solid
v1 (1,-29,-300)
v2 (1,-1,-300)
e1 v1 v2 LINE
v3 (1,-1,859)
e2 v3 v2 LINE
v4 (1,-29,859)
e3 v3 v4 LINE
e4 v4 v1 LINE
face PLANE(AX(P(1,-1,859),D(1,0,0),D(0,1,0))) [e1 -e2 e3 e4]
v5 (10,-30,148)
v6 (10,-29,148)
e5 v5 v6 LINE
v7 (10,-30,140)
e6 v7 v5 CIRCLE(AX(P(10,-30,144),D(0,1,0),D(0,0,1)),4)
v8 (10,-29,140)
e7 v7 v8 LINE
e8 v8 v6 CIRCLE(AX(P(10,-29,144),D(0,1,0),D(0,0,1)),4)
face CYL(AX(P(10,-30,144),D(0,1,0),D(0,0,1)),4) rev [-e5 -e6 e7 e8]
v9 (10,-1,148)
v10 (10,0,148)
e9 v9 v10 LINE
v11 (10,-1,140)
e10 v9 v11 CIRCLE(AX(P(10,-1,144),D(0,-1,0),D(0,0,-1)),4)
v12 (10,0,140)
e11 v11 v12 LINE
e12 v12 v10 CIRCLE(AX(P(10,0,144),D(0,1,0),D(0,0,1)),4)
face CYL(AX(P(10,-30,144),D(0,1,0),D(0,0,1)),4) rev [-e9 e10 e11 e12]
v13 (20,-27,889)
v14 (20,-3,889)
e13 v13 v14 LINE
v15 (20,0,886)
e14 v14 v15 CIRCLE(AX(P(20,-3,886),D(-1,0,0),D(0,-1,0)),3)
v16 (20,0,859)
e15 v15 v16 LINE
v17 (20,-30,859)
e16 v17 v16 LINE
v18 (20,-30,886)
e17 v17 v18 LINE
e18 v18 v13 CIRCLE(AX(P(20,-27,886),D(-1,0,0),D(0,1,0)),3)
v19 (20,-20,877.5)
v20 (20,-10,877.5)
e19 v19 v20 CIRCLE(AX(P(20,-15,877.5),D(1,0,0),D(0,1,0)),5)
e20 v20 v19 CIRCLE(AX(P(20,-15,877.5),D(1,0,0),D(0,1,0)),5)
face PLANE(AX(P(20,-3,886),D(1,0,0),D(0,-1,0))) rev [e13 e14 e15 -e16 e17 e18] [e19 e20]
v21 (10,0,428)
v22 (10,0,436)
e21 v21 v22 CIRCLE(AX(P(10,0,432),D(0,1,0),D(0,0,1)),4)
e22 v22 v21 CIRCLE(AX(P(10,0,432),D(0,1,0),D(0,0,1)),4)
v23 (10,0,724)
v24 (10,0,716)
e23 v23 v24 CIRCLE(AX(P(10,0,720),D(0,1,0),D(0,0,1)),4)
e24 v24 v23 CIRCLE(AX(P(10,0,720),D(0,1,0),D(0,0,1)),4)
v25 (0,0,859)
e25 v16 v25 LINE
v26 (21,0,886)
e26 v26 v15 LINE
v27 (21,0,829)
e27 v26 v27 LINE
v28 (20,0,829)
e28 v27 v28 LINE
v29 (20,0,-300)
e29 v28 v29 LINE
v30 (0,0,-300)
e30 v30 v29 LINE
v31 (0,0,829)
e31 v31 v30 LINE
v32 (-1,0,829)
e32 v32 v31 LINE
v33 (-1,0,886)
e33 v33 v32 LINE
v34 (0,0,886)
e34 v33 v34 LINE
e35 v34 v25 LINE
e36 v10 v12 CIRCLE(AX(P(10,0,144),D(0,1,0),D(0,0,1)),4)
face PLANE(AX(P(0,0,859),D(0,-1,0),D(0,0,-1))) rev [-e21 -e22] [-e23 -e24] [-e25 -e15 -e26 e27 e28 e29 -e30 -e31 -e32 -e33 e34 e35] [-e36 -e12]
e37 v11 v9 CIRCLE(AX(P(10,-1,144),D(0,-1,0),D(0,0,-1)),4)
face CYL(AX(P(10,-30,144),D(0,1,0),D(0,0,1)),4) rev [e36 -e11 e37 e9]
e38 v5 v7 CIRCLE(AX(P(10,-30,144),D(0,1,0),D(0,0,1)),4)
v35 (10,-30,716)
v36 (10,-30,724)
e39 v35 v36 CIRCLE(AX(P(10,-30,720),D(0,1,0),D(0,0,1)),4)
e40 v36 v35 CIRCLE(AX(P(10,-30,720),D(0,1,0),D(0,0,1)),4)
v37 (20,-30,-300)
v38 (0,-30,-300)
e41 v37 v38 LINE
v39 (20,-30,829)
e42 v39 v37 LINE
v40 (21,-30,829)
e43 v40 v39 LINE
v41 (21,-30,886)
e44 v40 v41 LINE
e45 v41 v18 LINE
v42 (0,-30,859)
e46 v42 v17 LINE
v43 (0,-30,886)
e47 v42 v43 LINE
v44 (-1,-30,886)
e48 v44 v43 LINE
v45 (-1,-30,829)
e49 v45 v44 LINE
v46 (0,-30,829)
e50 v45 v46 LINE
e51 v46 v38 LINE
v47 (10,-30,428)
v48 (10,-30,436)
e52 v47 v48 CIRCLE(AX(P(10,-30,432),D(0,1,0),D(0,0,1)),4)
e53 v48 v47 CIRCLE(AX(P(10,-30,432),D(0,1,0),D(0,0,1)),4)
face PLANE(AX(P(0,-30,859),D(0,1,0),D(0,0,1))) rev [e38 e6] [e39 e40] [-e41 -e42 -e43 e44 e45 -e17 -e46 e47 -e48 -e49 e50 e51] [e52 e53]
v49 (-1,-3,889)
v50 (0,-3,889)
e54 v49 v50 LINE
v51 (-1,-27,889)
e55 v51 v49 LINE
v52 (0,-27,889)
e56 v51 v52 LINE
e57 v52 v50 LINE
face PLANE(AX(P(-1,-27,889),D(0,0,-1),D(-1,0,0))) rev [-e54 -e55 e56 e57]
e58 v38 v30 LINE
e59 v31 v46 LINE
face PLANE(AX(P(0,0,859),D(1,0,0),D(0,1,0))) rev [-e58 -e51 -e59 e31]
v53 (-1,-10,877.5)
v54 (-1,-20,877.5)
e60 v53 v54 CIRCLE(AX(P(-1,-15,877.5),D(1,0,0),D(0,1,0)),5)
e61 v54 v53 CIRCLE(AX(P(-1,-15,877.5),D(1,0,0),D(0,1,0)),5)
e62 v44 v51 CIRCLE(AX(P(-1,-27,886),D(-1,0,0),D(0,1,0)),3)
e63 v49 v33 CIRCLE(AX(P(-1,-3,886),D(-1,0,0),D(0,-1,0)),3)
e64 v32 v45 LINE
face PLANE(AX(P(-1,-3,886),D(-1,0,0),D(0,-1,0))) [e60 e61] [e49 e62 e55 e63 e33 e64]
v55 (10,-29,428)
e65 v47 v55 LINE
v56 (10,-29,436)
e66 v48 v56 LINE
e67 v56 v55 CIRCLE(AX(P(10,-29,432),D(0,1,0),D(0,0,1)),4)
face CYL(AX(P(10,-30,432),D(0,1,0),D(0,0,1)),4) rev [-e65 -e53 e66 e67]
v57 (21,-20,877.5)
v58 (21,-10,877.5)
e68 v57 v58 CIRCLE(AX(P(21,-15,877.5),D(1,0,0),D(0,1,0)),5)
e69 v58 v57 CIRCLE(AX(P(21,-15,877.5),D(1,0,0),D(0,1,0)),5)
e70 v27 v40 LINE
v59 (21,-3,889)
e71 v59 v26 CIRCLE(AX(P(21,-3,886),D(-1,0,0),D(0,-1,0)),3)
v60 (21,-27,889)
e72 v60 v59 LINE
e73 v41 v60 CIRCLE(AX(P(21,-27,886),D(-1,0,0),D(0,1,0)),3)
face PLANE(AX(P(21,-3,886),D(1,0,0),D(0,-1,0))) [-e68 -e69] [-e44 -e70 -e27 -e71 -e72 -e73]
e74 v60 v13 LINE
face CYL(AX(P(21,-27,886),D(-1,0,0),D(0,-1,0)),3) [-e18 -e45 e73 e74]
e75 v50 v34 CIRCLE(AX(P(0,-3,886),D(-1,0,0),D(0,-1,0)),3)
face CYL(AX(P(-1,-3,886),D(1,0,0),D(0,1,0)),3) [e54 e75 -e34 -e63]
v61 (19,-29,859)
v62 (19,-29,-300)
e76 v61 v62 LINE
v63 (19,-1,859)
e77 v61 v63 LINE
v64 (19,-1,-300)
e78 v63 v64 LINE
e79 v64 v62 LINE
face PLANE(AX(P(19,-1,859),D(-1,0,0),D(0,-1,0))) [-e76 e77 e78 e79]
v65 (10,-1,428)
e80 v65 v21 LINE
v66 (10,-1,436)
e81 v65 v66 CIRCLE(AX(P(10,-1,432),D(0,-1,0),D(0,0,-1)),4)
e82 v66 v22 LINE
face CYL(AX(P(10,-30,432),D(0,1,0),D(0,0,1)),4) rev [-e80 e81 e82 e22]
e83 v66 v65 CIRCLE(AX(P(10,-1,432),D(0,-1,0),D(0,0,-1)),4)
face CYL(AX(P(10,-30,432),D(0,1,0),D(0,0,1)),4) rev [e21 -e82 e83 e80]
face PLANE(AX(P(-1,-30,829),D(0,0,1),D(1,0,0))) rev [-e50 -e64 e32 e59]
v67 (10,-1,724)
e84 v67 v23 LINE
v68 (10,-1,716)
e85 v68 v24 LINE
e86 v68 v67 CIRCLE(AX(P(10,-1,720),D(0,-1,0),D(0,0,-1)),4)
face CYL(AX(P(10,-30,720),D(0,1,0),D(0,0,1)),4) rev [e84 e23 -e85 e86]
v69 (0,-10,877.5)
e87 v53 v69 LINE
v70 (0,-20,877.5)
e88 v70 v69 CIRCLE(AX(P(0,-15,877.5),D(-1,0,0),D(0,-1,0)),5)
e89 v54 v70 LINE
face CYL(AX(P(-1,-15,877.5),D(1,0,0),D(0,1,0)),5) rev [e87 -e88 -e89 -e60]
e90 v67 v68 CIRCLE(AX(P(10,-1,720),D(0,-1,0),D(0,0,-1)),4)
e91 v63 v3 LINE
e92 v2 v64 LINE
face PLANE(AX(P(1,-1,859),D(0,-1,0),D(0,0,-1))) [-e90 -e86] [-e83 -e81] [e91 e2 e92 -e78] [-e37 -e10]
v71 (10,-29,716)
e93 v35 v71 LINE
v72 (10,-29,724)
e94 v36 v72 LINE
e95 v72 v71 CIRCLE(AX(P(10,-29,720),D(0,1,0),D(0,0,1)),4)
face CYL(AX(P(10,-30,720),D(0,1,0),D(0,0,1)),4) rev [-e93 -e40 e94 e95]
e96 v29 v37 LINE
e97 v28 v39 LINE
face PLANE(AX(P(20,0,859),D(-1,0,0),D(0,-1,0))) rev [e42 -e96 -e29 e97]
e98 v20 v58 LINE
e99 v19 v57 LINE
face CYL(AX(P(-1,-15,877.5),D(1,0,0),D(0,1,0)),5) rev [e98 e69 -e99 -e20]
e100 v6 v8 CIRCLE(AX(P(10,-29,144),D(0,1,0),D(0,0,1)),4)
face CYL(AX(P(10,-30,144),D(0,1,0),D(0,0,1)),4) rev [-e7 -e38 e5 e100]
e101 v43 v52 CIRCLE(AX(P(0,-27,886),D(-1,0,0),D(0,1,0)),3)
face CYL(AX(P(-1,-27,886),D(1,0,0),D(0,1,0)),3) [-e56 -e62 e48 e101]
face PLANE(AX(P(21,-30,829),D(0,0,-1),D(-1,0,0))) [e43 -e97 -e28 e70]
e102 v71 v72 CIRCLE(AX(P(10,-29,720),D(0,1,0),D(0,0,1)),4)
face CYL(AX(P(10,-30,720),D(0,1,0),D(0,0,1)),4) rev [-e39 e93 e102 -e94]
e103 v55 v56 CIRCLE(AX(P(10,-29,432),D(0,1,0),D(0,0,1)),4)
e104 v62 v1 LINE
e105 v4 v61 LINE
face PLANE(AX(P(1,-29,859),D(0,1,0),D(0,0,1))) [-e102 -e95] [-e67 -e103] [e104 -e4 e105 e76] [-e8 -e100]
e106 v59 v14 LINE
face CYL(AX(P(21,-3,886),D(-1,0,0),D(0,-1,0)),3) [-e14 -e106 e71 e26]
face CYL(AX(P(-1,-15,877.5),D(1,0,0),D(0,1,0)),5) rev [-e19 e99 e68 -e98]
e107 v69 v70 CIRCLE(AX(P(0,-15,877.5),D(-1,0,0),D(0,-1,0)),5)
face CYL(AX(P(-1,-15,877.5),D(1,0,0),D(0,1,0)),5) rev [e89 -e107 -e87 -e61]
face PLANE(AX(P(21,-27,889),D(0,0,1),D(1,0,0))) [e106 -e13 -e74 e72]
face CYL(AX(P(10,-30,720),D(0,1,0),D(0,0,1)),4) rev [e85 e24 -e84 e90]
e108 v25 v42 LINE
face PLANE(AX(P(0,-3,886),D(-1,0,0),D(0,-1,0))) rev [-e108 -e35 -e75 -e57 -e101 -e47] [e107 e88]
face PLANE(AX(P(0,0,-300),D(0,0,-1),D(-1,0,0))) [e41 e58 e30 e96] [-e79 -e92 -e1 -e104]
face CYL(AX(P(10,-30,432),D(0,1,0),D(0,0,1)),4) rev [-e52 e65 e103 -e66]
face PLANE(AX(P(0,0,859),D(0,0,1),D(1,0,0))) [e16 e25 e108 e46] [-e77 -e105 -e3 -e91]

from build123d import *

# Parameters (mm, degrees)
SKETCH1_W           = 20
SKETCH1_H           = 30
SKETCH1_W_2         = 18
SKETCH1_H_2         = 28
BOSS_EXTRUDE1_DEPTH = 859
BOSS_EXTRUDE2_DEPTH = 1
SKETCH4_R           = 5
CUT_EXTRUDE1_DEPTH  = 890.778062216
SKETCH5_R           = 4
CUT_EXTRUDE2_DEPTH  = 890.753898558
SKETCH6_W           = 20
SKETCH6_H           = 30
SKETCH6_W_2         = 18
SKETCH6_H_2         = 28
BOSS_EXTRUDE3_DEPTH = 300


with BuildPart() as part:
    # Sketch1 → Boss-Extrude1 (new body)
    with BuildSketch(Plane.XY):
        with Locations((10, -15)):
            Rectangle(SKETCH1_W, SKETCH1_H)
        with Locations((10, -15)):
            Rectangle(SKETCH1_W_2, SKETCH1_H_2, mode=Mode.SUBTRACT)
    extrude(amount=BOSS_EXTRUDE1_DEPTH)

    # Sketch3 → Boss-Extrude2 (add)
    with BuildSketch(Plane.ZY):
        with BuildLine():
            Line((829, -30), (859, -30))
            Line((859, -30), (886, -30))
            ThreePointArc((886, -30), (888.121320344, -29.121320344), (889, -27))
            Line((889, -27), (889, -3))
            ThreePointArc((889, -3), (888.121320344, -0.878679656), (886, 0))
            Line((886, 0), (859, 0))
            Line((859, 0), (829, 0))
            Line((829, 0), (829, -30))
        make_face()
    boss_extrude2 = extrude(amount=BOSS_EXTRUDE2_DEPTH)

    # Mirror2: Boss-Extrude2 across plane
    add(boss_extrude2.mirror(Plane(origin=(10, 0, 0), x_dir=(0, 0, 1), z_dir=(1, 0, 0))))

    # Sketch4 → Cut-Extrude1 (cut, through all)
    with BuildSketch(Plane(origin=(21, 0, 0), x_dir=(0, 0, -1), z_dir=(1, 0, 0))):
        with Locations(Location((-877.5, -15, 0), (0, 0, 90))):
            Circle(SKETCH4_R)
    extrude(amount=-CUT_EXTRUDE1_DEPTH, mode=Mode.SUBTRACT)

    # Sketch5 → Cut-Extrude2 (cut, through all)
    with BuildSketch(Plane(origin=(0, 0, 0), x_dir=(1, 0, 0), z_dir=(0, 1, 0))):
        with Locations(Location((10, -144, 0), (0, 0, 270))):
            Circle(SKETCH5_R)
        with Locations(Location((10, -432, 0), (0, 0, 270))):
            Circle(SKETCH5_R)
        with Locations(Location((10, -720, 0), (0, 0, 270))):
            Circle(SKETCH5_R)
    extrude(amount=-CUT_EXTRUDE2_DEPTH, mode=Mode.SUBTRACT)

    # Sketch6 → Boss-Extrude3 (add)
    with BuildSketch(Plane(origin=(0, 0, 0), x_dir=(-1, 0, 0), z_dir=(0, 0, -1))):
        with Locations((-10, -15)):
            Rectangle(SKETCH6_W, SKETCH6_H)
        with Locations((-10, -15)):
            Rectangle(SKETCH6_W_2, SKETCH6_H_2, mode=Mode.SUBTRACT)
    extrude(amount=BOSS_EXTRUDE3_DEPTH)


solid = part.part
